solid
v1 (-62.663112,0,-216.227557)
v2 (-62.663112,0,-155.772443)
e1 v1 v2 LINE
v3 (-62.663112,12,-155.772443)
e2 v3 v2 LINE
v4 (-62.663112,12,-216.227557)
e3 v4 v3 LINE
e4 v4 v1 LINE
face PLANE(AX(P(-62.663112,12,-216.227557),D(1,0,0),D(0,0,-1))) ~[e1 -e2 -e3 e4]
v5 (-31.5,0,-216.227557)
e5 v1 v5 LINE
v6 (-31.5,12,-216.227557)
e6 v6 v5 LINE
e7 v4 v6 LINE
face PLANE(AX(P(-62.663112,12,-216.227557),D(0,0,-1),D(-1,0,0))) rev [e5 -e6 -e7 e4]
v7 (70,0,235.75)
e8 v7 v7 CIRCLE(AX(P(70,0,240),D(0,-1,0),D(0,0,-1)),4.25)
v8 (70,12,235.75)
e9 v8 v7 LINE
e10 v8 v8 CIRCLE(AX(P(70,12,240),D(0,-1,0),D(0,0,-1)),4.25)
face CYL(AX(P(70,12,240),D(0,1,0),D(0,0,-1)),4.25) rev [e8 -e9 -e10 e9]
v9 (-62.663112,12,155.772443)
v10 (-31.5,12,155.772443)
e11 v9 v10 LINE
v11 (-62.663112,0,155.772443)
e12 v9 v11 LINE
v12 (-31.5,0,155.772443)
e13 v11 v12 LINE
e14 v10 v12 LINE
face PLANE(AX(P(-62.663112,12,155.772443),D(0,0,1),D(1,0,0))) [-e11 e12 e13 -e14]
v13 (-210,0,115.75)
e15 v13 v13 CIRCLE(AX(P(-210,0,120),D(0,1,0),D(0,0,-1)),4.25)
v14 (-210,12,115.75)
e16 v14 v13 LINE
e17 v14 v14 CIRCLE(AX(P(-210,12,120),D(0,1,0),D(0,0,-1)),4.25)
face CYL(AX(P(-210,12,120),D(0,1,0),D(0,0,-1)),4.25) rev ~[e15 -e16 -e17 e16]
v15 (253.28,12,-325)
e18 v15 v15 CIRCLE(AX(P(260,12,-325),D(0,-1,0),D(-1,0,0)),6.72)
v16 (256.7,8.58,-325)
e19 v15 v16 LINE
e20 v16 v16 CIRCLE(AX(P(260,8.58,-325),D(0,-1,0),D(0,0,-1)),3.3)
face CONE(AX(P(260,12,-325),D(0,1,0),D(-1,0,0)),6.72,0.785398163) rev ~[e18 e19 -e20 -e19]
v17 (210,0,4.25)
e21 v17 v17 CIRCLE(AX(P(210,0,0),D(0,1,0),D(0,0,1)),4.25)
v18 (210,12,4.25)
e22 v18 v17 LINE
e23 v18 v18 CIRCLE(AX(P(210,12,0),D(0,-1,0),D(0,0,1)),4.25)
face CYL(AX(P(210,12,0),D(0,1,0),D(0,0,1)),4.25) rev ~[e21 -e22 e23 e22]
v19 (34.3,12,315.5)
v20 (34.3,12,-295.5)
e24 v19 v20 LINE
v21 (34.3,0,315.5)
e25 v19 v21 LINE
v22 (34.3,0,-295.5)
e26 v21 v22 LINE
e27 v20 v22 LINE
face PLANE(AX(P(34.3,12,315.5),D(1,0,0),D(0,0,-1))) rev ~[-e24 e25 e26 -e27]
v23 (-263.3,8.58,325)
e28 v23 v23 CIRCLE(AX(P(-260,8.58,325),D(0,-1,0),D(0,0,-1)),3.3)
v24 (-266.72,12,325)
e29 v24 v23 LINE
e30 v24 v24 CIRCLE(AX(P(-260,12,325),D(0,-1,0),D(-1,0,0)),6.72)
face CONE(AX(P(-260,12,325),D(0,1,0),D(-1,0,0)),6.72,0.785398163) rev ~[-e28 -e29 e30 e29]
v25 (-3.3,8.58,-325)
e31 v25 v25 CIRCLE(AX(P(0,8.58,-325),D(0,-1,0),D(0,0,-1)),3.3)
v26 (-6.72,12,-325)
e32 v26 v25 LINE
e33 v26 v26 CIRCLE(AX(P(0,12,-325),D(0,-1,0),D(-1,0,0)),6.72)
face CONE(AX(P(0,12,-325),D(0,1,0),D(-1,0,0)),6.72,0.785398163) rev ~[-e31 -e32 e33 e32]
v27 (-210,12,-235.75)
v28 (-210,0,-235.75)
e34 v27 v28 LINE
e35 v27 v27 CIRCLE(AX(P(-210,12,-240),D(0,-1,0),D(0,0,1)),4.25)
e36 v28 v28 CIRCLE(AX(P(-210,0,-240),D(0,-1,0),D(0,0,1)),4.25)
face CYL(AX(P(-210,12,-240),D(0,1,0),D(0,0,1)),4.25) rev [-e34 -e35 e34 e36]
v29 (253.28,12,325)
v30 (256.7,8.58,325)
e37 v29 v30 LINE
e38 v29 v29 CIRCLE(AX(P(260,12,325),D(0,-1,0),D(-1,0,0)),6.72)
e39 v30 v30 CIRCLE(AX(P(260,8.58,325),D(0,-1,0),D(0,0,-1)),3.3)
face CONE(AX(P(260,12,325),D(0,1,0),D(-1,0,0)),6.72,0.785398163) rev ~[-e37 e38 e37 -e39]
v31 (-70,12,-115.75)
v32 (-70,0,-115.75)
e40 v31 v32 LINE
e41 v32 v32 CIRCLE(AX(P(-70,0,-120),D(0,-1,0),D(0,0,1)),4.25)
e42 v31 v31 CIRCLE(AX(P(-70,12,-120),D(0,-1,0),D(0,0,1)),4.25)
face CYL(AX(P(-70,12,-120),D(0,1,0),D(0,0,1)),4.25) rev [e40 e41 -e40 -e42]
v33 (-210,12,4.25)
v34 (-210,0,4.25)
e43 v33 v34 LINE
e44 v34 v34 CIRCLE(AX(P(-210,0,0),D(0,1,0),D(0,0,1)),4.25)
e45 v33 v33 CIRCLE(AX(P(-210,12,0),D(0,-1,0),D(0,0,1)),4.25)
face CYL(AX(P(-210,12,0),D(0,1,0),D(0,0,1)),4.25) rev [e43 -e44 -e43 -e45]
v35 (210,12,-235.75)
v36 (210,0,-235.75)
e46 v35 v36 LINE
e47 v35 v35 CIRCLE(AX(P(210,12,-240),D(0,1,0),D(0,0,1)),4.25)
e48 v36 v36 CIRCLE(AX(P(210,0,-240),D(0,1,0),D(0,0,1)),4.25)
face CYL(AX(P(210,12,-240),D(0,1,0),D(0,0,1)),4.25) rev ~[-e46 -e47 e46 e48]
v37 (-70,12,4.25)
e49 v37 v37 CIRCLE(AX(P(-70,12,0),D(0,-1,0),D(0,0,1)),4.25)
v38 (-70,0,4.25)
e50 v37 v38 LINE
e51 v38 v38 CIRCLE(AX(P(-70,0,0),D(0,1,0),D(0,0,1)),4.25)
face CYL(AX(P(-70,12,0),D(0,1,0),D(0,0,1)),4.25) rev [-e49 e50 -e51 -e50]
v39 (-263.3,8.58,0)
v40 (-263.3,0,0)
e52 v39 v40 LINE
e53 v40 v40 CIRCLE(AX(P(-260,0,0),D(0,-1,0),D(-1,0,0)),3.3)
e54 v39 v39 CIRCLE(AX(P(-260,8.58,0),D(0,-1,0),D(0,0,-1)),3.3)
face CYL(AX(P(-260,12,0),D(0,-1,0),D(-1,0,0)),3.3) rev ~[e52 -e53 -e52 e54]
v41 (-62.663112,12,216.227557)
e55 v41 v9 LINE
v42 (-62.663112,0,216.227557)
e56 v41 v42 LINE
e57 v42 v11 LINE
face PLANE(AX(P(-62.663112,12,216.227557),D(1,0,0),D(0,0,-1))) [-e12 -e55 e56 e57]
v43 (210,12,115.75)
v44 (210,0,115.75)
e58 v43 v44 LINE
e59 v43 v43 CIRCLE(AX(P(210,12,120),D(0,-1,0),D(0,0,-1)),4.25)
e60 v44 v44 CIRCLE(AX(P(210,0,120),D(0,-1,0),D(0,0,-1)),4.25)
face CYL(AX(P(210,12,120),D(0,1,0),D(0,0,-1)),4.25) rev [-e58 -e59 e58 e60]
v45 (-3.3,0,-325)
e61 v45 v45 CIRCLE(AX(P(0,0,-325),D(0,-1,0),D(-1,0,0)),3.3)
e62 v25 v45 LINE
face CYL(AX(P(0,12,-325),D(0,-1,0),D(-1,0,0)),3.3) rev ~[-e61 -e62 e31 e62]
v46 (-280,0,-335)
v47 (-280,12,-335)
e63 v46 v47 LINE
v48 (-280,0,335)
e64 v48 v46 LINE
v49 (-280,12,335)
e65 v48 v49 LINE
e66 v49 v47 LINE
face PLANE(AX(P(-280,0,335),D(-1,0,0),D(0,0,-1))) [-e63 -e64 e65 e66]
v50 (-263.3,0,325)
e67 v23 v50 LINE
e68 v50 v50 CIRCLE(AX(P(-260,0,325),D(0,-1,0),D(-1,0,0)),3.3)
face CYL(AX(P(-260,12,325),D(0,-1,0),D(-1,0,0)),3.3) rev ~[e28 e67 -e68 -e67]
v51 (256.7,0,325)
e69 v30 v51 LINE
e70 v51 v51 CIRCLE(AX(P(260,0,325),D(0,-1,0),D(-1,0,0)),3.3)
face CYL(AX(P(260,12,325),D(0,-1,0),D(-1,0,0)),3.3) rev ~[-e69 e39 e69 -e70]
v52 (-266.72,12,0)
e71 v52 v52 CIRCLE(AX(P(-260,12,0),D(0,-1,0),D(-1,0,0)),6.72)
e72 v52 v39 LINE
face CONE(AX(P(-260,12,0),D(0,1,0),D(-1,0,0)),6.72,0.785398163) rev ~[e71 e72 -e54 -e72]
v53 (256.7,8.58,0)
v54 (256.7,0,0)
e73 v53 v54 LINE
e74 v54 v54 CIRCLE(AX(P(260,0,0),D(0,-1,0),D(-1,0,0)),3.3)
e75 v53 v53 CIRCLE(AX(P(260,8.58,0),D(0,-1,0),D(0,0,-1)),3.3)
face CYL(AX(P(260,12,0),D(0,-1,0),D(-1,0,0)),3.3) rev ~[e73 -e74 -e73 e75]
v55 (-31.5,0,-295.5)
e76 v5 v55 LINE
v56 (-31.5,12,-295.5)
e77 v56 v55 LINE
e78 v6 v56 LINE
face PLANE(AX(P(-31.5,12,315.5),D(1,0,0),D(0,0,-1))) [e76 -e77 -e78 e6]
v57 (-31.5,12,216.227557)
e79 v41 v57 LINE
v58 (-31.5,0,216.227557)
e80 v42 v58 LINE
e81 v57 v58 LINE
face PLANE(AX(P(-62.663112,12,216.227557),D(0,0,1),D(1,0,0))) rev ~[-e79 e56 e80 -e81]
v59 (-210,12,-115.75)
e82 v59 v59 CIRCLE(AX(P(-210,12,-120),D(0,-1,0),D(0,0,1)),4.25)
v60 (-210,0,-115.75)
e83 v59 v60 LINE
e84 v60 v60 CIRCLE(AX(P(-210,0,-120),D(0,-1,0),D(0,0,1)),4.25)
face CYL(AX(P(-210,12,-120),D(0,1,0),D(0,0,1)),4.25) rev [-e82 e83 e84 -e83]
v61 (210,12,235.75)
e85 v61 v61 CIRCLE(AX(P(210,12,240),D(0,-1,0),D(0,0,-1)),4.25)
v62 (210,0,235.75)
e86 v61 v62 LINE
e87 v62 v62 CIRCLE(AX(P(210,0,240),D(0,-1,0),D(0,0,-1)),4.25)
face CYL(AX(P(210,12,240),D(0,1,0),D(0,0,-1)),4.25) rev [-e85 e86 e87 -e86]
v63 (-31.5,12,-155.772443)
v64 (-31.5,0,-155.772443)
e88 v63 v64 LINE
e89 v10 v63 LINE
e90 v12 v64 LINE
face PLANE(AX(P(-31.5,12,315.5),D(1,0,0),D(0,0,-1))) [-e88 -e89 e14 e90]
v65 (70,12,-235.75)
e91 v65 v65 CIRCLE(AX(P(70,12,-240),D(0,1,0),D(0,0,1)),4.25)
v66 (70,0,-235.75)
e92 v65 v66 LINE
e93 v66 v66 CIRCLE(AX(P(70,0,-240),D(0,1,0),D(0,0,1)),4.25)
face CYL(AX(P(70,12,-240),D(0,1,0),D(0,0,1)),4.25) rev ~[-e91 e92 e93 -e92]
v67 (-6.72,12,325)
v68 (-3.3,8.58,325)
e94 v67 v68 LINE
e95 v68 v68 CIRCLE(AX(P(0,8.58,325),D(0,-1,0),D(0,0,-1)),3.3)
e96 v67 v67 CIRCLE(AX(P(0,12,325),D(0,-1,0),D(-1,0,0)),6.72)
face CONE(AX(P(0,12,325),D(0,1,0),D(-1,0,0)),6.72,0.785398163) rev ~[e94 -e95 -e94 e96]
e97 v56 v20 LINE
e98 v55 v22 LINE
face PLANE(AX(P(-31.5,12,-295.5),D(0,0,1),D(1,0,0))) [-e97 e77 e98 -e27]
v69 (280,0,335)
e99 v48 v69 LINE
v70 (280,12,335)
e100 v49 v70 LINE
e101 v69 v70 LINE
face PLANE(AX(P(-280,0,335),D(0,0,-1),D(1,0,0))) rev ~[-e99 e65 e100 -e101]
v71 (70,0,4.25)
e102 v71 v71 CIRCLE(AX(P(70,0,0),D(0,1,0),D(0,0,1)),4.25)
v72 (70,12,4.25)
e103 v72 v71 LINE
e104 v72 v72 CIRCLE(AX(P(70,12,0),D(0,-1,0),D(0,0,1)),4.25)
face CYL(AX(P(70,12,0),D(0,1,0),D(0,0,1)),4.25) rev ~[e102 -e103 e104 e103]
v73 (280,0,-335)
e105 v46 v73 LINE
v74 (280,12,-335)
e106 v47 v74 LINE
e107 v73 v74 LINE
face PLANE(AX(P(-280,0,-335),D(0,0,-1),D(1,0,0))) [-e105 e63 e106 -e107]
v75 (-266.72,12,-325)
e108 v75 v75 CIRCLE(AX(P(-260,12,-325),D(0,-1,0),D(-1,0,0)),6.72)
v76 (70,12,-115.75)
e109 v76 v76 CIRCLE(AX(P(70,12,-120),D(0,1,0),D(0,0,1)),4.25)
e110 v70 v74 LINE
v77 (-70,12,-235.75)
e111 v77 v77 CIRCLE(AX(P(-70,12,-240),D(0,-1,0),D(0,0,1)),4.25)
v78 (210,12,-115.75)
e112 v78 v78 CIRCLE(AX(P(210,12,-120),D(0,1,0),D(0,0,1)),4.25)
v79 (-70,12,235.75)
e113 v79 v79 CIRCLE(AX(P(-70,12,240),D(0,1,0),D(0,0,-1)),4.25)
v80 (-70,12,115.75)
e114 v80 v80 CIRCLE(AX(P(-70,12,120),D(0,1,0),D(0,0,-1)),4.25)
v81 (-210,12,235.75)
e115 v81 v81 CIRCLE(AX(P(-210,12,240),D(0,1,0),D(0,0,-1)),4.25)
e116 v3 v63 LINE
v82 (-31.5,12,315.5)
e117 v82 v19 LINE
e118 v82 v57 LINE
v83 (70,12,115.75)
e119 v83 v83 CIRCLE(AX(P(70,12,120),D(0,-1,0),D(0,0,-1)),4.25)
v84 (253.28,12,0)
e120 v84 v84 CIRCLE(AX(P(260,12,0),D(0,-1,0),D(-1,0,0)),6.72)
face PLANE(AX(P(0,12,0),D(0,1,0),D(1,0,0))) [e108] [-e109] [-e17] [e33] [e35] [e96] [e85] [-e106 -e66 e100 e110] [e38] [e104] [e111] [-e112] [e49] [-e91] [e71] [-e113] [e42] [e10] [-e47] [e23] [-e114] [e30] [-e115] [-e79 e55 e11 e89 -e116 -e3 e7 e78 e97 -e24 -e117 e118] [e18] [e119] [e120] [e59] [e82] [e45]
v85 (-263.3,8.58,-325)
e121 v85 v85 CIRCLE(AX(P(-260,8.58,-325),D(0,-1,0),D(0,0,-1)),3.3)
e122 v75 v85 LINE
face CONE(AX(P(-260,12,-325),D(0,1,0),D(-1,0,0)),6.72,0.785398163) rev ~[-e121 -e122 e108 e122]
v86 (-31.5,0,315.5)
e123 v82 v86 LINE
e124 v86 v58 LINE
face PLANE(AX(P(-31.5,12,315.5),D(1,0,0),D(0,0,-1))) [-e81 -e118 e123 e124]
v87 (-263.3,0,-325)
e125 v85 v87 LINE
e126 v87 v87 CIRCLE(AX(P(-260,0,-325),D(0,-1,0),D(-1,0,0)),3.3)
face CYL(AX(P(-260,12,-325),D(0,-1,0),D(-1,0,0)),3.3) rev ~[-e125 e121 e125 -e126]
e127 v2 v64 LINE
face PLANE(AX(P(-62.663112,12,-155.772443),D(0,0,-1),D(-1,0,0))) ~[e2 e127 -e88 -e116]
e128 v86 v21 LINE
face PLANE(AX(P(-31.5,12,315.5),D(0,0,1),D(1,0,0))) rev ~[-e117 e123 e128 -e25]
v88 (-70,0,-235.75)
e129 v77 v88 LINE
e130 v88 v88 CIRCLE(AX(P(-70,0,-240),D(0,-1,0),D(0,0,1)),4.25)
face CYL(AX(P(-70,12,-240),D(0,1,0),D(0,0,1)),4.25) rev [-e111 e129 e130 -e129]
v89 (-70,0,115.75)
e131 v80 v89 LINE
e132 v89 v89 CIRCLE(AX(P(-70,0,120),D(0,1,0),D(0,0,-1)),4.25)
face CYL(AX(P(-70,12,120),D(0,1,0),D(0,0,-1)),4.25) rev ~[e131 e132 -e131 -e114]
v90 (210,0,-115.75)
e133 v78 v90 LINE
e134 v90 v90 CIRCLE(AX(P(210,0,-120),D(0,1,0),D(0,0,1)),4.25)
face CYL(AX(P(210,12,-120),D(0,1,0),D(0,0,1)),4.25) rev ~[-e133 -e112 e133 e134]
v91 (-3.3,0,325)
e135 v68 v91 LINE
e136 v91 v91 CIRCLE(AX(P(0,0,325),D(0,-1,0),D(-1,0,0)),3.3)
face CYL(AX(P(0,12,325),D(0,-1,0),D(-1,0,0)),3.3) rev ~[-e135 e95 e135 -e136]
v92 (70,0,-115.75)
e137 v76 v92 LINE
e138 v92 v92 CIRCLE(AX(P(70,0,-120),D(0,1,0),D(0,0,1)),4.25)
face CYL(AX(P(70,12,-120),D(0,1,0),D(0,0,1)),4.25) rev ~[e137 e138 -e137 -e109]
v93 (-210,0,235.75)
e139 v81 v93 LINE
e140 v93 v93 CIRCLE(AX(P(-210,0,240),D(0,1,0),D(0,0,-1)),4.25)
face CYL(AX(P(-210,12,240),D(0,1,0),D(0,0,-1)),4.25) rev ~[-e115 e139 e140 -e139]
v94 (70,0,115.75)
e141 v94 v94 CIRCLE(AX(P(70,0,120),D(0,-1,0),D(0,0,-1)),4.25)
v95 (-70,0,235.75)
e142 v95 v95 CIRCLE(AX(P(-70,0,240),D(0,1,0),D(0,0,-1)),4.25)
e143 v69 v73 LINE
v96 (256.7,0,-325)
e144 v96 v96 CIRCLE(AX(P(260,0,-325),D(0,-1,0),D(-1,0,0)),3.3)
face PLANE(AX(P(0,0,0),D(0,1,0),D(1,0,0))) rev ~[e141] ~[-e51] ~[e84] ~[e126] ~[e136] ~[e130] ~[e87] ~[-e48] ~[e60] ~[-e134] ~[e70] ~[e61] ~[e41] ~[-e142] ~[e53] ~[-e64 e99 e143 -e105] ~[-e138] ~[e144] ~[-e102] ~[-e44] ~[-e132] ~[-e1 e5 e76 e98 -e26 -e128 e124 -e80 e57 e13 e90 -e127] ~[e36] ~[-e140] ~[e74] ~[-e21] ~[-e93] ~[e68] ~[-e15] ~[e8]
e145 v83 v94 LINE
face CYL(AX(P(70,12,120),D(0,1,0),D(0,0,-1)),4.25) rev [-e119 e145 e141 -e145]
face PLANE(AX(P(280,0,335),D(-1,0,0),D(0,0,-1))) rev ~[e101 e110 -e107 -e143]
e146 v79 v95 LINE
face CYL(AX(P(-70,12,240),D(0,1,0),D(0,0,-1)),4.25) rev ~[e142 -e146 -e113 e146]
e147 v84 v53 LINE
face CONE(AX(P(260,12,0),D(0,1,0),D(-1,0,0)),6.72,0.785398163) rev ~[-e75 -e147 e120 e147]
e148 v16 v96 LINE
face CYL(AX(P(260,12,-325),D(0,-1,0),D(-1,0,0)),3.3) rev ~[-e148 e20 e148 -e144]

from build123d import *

# Parameters (mm, degrees)
SKETCH1_W                     = 560
SKETCH1_H                     = 670
BOSS_EXTRUDE1_DEPTH           = 12
SKETCH3_R                     = 4.25
SKETCH3_R_2                   = 0.639613625
CUT_EXTRUDE1_DEPTH            = 12
MIRROR2_COPY_1_SKETCH_R       = 4.25
MIRROR2_COPY_1_SKETCH_R_2     = 0.639613625
MIRROR2_COPY_1_DEPTH          = 12
CSK_FOR_M6_SFHCS1_D           = 6.6
CSK_FOR_M6_SFHCS1_CSINK_D     = 13.44
CSK_FOR_M6_SFHCS1_CSINK_ANGLE = 90
SKETCH10_W                    = 65.8
SKETCH10_H                    = 611
CUT_EXTRUDE2_DEPTH            = 111
SKETCH11_W                    = 31.663111861
SKETCH11_H                    = 60.455114524
CUT_EXTRUDE3_DEPTH            = 55


with BuildPart() as part:
    # Sketch1 → Boss-Extrude1 (new body)
    with BuildSketch(Plane(origin=(0, 0, 0), x_dir=(1, 0, 0), z_dir=(0, 1, 0))):
        Rectangle(SKETCH1_W, SKETCH1_H)
    extrude(amount=BOSS_EXTRUDE1_DEPTH)

    # Sketch3 → Cut-Extrude1 (cut)
    with BuildSketch(Plane(origin=(0, 12, 0), x_dir=(1, 0, 0), z_dir=(0, 1, 0))):
        with Locations(Location((210, 240, 0), (0, 0, 270))):
            Circle(SKETCH3_R)
        with Locations(Location((70, 240, 0), (0, 0, 270))):
            Circle(SKETCH3_R)
        with Locations(Location((210, 120, 0), (0, 0, 270))):
            Circle(SKETCH3_R)
        with Locations(Location((70, 120, 0), (0, 0, 270))):
            Circle(SKETCH3_R)
        with Locations(Location((70, 0, 0), (0, 0, 270))):
            Circle(SKETCH3_R)
        with Locations(Location((210, 0, 0), (0, 0, 270))):
            Circle(SKETCH3_R)
        with Locations(Location((0, 0, 0), (0, 0, 270))):
            Circle(SKETCH3_R_2)
    cut_extrude1 = extrude(amount=-CUT_EXTRUDE1_DEPTH, mode=Mode.SUBTRACT)

    # Mirror1: Cut-Extrude1 across plane
    add(cut_extrude1.mirror(Plane(origin=(0, 0, 0), x_dir=(0, 0, 1), z_dir=(1, 0, 0))), mode=Mode.SUBTRACT)

    # Mirror2: Cut-Extrude1 across plane
    add(cut_extrude1.mirror(Plane.XY), mode=Mode.SUBTRACT)

    # Mirror2 copy 1 sketch → Mirror2 copy 1 (cut)
    with BuildSketch(Plane(origin=(0, 12, 0), x_dir=(-1, 0, 0), z_dir=(0, 1, 0))):
        with Locations(Location((210, 240, 0), (0, 0, 270))):
            Circle(MIRROR2_COPY_1_SKETCH_R)
        with Locations(Location((70, 240, 0), (0, 0, 270))):
            Circle(MIRROR2_COPY_1_SKETCH_R)
        with Locations(Location((210, 120, 0), (0, 0, 270))):
            Circle(MIRROR2_COPY_1_SKETCH_R)
        with Locations(Location((70, 120, 0), (0, 0, 270))):
            Circle(MIRROR2_COPY_1_SKETCH_R)
        with Locations(Location((70, 0, 0), (0, 0, 270))):
            Circle(MIRROR2_COPY_1_SKETCH_R)
        with Locations(Location((210, 0, 0), (0, 0, 270))):
            Circle(MIRROR2_COPY_1_SKETCH_R)
        with Locations(Location((0, 0, 0), (0, 0, 270))):
            Circle(MIRROR2_COPY_1_SKETCH_R_2)
    extrude(amount=-MIRROR2_COPY_1_DEPTH, mode=Mode.SUBTRACT)

    # CSK for M6 SFHCS1 (through all)
    with Locations(Plane(origin=(0, 12, 0), x_dir=(1, 0, 0), z_dir=(0, 1, 0))):
        with Locations((0, 0), (260, 0), (0, 325), (260, 325), (0, -325), (-260, 0), (-260, 325), (-260, -325), (260, -325)):
            CounterSinkHole(CSK_FOR_M6_SFHCS1_D / 2, CSK_FOR_M6_SFHCS1_CSINK_D / 2, counter_sink_angle=CSK_FOR_M6_SFHCS1_CSINK_ANGLE)

    # Sketch10 → Cut-Extrude2 (cut)
    with BuildSketch(Plane(origin=(0, 12, 0), x_dir=(1, 0, 0), z_dir=(0, 1, 0))):
        with Locations((1.4, -10)):
            Rectangle(SKETCH10_W, SKETCH10_H)
    extrude(amount=-CUT_EXTRUDE2_DEPTH, mode=Mode.SUBTRACT)

    # Sketch11 → Cut-Extrude3 (cut)
    with BuildSketch(Plane(origin=(0, 12, 0), x_dir=(1, 0, 0), z_dir=(0, 1, 0))):
        with Locations((-46.831555931, -186)):
            Rectangle(SKETCH11_W, SKETCH11_H)
    cut_extrude3 = extrude(amount=-CUT_EXTRUDE3_DEPTH, mode=Mode.SUBTRACT)

    # Mirror3: Cut-Extrude3 across plane
    add(cut_extrude3.mirror(Plane.XY), mode=Mode.SUBTRACT)


solid = part.part
